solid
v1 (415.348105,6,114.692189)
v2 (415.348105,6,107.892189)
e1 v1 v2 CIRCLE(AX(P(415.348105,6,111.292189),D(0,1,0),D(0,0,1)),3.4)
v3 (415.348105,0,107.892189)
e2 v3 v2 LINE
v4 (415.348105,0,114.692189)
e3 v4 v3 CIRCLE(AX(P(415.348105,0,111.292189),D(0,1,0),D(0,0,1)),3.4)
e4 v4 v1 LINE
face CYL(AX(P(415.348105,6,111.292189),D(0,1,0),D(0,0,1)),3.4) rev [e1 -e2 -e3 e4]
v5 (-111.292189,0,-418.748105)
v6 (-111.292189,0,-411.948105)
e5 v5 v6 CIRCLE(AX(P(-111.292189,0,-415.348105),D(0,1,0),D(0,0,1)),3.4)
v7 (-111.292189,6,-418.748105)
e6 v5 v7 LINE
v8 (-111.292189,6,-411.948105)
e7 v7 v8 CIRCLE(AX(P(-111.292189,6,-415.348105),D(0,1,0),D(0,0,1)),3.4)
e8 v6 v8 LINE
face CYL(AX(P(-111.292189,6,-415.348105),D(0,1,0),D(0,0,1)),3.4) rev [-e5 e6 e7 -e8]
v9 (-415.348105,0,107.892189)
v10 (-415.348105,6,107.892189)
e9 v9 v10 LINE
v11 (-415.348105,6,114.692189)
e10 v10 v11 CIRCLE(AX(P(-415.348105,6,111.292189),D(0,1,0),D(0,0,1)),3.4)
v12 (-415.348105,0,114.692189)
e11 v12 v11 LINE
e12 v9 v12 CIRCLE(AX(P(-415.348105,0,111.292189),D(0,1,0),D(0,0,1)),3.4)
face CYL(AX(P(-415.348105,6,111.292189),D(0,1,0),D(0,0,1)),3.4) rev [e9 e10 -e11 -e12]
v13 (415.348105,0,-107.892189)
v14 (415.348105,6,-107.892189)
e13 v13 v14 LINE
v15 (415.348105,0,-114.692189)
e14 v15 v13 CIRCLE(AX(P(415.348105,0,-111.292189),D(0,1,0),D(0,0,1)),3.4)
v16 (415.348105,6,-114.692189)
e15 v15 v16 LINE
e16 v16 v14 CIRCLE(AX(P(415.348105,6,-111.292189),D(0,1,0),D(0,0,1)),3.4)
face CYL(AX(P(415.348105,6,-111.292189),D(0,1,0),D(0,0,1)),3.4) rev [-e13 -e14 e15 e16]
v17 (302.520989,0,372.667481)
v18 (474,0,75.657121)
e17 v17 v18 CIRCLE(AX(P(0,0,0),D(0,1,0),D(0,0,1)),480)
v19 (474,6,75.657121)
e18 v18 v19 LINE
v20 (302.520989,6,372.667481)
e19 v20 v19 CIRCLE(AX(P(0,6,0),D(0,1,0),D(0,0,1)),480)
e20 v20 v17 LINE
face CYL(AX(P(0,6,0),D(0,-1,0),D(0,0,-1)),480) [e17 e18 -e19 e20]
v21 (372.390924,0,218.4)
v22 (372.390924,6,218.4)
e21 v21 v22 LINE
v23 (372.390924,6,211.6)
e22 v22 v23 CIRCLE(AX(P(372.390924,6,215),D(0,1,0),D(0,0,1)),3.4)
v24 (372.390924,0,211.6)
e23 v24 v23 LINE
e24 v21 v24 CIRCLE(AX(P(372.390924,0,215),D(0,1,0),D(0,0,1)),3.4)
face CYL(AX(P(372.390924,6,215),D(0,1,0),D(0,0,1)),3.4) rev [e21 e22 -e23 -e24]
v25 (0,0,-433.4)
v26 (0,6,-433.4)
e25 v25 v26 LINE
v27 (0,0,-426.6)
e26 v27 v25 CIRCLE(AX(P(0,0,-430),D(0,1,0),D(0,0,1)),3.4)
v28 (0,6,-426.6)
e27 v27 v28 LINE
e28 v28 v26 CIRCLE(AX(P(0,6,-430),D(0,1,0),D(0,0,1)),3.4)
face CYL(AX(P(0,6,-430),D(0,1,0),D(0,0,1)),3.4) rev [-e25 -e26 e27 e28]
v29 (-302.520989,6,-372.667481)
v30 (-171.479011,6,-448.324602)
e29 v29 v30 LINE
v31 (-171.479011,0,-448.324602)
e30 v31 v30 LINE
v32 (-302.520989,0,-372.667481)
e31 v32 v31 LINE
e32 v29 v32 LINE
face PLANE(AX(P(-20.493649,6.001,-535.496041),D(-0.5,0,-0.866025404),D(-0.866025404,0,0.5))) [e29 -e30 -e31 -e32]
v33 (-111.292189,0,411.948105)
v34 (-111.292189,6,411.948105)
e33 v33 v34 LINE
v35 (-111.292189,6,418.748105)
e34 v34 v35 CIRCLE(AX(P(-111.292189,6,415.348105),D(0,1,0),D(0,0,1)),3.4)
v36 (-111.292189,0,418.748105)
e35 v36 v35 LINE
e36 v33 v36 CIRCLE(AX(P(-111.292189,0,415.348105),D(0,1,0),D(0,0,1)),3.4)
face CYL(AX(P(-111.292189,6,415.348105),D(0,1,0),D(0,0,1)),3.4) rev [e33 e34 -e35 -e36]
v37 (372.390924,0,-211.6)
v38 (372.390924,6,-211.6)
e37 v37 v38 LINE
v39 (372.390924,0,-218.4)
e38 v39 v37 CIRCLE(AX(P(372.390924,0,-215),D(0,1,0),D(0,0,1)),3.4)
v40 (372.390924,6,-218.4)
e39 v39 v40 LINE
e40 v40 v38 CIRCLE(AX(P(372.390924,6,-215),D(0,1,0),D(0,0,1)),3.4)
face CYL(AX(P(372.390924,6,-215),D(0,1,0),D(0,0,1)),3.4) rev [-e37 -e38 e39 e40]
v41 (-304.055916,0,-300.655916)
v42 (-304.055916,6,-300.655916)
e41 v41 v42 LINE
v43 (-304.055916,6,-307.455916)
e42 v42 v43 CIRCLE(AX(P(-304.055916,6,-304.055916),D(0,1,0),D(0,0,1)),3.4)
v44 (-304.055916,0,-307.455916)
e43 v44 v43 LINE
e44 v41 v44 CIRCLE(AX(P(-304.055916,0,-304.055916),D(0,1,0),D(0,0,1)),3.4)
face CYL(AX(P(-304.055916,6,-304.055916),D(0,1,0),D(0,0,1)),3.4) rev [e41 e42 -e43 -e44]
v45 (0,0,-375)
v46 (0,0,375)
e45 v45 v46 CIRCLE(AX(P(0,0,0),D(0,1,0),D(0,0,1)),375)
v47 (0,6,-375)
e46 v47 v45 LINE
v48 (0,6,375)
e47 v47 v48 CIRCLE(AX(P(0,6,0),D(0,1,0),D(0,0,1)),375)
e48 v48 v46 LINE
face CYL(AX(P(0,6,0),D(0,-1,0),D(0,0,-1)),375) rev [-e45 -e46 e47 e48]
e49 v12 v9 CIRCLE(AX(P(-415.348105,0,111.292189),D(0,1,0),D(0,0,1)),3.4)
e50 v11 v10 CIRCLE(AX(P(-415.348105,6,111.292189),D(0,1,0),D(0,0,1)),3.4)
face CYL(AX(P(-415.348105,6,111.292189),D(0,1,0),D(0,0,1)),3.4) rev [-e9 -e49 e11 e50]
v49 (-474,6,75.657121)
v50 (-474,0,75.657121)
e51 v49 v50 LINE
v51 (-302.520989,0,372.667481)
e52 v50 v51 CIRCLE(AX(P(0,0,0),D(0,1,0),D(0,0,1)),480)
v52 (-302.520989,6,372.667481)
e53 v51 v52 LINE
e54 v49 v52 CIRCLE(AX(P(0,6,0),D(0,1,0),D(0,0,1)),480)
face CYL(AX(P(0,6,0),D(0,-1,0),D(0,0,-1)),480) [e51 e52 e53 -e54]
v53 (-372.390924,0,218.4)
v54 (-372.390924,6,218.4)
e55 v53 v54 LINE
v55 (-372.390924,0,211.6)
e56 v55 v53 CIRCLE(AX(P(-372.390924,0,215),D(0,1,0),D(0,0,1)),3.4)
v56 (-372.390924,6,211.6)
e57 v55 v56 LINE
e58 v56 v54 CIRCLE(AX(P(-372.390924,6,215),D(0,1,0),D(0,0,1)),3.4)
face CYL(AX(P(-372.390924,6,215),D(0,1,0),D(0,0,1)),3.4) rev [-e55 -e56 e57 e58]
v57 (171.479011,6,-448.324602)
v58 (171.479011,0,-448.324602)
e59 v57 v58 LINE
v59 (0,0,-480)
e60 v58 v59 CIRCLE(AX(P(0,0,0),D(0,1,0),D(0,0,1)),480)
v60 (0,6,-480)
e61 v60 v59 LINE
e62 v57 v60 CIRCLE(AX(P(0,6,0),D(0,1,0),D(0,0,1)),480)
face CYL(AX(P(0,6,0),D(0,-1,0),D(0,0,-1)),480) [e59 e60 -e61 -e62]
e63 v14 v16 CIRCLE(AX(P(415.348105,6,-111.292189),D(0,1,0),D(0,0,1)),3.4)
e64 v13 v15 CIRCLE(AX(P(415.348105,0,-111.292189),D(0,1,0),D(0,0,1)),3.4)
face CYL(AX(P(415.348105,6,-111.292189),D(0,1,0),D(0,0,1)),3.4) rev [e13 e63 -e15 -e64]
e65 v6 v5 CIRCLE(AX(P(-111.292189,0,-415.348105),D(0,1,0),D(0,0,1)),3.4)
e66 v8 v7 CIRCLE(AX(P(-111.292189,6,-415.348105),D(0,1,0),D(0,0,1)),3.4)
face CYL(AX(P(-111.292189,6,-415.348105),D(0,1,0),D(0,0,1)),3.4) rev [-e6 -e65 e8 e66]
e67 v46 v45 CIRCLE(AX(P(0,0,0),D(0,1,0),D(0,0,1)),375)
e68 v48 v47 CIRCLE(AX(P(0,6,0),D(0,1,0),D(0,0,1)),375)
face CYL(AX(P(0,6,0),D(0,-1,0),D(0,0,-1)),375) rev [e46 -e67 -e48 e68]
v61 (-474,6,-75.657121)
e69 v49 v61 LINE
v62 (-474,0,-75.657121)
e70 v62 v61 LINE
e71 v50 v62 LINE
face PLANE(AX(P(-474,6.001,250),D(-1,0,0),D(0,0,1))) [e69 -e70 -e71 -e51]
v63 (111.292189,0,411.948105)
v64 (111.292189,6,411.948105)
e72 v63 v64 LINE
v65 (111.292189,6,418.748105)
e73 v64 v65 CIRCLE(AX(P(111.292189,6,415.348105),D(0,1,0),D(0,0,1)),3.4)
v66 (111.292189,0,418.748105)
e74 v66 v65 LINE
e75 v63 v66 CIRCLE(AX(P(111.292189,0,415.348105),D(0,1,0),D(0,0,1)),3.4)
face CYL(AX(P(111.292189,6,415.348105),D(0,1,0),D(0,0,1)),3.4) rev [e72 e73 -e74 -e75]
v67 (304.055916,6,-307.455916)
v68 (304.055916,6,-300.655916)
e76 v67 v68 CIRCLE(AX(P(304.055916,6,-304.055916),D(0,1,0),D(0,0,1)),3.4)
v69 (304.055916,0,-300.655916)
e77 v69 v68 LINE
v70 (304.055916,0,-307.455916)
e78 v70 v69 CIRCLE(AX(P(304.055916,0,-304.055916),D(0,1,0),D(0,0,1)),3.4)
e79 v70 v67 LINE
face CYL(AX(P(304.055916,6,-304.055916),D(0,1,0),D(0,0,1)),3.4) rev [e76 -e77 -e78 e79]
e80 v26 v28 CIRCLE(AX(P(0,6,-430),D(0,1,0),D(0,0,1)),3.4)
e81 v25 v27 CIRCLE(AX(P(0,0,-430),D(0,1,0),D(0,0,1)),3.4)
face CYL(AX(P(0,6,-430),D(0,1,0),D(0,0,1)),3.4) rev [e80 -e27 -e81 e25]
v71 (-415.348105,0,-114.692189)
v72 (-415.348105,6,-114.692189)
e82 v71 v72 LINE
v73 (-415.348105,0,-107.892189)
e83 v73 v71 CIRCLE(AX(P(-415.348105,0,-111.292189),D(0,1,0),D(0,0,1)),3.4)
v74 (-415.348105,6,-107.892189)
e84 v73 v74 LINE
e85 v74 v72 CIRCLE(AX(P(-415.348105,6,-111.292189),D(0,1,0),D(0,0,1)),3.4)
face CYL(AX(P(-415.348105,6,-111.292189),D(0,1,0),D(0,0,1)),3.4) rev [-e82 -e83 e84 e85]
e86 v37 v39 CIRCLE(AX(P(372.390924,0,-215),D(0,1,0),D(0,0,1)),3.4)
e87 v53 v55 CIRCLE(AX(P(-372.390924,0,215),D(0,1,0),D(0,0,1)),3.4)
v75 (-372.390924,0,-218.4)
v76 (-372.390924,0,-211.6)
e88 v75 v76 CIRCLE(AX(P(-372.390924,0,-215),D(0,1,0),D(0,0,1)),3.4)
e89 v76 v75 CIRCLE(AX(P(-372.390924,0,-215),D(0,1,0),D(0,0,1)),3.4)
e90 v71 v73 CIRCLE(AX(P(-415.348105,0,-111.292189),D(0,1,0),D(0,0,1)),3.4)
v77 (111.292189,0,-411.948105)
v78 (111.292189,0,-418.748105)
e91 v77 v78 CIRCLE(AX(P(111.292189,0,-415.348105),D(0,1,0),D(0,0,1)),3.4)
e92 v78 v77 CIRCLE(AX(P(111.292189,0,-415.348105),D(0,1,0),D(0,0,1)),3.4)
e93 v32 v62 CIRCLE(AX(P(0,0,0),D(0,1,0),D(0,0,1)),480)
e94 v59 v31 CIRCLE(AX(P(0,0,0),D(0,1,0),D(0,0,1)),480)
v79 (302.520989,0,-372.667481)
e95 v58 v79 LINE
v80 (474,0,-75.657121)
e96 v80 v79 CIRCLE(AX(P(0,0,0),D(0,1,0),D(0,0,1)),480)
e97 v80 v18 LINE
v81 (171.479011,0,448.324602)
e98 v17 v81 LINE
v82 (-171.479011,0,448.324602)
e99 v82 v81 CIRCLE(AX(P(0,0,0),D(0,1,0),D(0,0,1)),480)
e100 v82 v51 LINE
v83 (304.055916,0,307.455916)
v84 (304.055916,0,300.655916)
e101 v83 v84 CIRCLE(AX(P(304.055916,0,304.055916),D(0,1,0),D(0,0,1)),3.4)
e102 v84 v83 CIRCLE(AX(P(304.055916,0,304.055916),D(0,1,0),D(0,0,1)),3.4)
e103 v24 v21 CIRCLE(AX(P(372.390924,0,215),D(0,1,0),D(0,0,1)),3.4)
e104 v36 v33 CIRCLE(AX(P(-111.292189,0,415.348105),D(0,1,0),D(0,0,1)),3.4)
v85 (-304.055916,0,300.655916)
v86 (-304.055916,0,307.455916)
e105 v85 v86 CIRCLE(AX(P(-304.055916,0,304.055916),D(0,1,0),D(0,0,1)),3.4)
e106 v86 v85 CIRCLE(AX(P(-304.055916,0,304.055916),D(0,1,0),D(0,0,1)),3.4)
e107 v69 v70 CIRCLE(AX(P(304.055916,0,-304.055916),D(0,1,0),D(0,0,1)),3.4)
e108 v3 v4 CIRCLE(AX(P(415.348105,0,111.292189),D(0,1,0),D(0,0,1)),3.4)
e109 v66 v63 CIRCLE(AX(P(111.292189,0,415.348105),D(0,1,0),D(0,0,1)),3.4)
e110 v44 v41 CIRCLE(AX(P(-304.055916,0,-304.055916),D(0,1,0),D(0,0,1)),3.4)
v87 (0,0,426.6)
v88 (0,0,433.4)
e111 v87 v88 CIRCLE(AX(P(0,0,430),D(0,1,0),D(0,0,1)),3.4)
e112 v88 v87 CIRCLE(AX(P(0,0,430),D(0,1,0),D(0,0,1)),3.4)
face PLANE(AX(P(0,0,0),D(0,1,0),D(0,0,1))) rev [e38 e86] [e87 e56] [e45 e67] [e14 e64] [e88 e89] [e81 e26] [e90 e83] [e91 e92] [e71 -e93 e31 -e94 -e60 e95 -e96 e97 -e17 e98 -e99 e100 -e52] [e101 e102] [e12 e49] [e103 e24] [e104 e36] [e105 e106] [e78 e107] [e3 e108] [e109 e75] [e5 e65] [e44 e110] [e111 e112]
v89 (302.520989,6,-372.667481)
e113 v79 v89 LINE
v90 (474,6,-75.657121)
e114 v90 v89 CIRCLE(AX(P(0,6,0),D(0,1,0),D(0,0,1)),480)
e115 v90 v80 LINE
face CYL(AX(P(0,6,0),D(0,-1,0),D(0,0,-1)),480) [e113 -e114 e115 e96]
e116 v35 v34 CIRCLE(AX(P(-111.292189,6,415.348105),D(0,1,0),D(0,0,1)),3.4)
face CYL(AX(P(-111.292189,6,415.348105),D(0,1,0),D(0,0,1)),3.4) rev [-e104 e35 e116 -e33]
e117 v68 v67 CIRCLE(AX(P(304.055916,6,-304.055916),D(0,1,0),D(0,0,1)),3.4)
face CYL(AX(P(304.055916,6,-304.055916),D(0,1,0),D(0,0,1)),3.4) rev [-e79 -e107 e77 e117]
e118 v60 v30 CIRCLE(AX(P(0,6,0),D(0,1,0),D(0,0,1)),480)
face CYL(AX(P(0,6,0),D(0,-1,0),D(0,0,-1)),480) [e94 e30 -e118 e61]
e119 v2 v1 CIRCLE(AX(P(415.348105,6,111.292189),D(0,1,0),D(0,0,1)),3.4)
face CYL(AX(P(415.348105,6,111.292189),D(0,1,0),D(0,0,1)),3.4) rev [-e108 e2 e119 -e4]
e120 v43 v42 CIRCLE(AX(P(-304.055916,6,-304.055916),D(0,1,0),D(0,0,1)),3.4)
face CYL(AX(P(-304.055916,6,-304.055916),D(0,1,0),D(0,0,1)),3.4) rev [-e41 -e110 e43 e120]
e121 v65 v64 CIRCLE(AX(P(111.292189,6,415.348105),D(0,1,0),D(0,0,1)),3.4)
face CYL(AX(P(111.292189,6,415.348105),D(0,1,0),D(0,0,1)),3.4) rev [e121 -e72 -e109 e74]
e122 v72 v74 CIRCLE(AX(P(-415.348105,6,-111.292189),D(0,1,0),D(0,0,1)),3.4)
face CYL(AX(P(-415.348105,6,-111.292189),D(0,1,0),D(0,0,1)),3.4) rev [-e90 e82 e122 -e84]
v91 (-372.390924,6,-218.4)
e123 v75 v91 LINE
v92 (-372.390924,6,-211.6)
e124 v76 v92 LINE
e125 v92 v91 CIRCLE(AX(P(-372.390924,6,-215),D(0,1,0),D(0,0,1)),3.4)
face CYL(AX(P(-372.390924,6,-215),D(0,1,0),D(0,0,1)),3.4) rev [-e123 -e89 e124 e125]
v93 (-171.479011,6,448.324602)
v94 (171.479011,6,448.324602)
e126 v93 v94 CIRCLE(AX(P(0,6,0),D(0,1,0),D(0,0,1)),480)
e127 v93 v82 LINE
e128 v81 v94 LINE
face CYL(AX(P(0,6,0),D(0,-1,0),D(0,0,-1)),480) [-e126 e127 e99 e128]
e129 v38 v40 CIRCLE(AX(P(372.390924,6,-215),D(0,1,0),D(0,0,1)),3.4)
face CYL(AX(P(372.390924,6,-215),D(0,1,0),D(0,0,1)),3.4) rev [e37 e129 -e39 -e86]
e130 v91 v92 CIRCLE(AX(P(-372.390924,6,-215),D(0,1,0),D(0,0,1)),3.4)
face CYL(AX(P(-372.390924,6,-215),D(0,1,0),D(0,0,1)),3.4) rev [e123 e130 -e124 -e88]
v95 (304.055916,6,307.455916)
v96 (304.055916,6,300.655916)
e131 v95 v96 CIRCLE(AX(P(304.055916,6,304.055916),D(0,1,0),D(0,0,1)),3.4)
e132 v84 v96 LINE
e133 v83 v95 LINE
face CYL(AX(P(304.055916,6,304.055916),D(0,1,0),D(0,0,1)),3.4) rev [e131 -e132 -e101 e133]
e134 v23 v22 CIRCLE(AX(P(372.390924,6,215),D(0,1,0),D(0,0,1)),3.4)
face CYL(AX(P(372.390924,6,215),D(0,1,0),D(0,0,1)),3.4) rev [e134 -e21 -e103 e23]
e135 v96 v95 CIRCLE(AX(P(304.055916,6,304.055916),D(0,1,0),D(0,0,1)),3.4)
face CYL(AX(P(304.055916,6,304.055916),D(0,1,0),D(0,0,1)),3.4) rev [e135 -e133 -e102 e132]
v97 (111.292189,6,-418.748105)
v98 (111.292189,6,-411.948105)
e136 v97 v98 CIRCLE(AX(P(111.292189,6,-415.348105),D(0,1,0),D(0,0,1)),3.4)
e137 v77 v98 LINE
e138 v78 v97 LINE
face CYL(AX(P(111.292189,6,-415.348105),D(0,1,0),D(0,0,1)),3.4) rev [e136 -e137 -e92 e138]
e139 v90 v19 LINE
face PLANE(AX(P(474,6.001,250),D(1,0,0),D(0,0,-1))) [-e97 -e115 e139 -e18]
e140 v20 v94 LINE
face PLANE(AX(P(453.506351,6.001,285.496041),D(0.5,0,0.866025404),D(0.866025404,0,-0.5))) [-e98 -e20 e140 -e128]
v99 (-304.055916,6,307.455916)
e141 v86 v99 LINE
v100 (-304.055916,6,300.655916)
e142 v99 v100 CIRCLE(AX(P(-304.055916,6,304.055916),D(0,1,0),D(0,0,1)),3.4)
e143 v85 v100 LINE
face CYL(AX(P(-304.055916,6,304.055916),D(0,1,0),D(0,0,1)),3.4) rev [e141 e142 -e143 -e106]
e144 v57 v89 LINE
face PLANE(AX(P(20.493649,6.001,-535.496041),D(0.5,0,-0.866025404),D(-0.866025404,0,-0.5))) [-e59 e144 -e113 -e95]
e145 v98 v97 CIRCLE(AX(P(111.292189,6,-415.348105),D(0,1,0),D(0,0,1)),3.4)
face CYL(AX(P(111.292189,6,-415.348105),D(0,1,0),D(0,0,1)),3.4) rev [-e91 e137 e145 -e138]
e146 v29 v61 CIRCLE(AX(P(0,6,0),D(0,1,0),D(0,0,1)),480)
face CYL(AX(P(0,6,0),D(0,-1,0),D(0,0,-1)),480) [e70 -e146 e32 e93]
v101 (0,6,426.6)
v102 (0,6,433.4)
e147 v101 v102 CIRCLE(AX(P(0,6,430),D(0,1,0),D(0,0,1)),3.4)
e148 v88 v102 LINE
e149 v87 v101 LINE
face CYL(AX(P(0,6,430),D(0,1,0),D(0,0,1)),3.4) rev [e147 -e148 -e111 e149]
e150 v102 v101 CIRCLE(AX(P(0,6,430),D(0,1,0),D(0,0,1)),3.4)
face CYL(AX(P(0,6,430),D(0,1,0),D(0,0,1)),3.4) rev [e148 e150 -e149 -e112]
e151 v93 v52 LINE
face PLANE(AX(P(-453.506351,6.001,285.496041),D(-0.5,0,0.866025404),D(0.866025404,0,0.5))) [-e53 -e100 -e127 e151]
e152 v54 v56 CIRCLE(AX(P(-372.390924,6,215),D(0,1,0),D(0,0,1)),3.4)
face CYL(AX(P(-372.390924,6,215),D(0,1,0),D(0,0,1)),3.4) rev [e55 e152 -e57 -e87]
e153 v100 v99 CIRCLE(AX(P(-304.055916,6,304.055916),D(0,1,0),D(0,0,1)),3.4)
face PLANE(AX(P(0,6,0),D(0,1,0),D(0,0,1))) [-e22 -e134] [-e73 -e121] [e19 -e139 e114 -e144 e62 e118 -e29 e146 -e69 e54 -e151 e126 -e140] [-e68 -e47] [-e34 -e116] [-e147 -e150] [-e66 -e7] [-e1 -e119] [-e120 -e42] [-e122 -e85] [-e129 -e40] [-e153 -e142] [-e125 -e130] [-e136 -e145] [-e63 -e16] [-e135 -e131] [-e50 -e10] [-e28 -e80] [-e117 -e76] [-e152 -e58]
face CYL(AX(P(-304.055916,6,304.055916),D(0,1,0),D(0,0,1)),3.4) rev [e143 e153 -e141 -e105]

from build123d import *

# Parameters (mm, degrees)
SKETCH1_R             = 480
SKETCH1_R_2           = 375
BOSS_EXTRUDE1_DEPTH   = 6
CUT_EXTRUDE3_REACH    = 680.849
SKETCH2_W             = 12
SKETCH2_H             = 500
CIRPATTERN1_COUNT     = 3
M8_TAPPED_HOLE1_D     = 6.8
M8_TAPPED_HOLE1_DEPTH = 6


with BuildPart() as part:
    # Sketch1 → Boss-Extrude1 (new body)
    with BuildSketch(Plane(origin=(0, 0, 0), x_dir=(1, 0, 0), z_dir=(0, 1, 0))):
        with Locations(Location((0, 0, 0), (0, 0, 270))):
            Circle(SKETCH1_R)
        with Locations(Location((0, 0, 0), (0, 0, 270))):
            Circle(SKETCH1_R_2, mode=Mode.SUBTRACT)
    extrude(amount=BOSS_EXTRUDE1_DEPTH)

    # Sketch2 → Cut-Extrude3 (cut, up to next)
    with BuildSketch(Plane(origin=(0, 0, 0), x_dir=(1, 0, 0), z_dir=(0, 1, 0)), mode=Mode.PRIVATE) as cut_extrude3_sk1:
        with Locations((-480, 0)):
            Rectangle(SKETCH2_W, SKETCH2_H)
    cut_extrude3_tool1 = extrude(cut_extrude3_sk1.sketch, amount=CUT_EXTRUDE3_REACH, mode=Mode.PRIVATE) & part.part
    # Sketch2 → Cut-Extrude3 (cut, up to next)
    with BuildSketch(Plane(origin=(0, 0, 0), x_dir=(1, 0, 0), z_dir=(0, 1, 0)), mode=Mode.PRIVATE) as cut_extrude3_sk2:
        with Locations((480, 0)):
            Rectangle(SKETCH2_W, SKETCH2_H)
    cut_extrude3_tool2 = extrude(cut_extrude3_sk2.sketch, amount=CUT_EXTRUDE3_REACH, mode=Mode.PRIVATE) & part.part
    cut_extrude3_1 = cut_extrude3_tool1.solids().sort_by_distance((-480, 0, 0))[0]
    add(cut_extrude3_1, mode=Mode.SUBTRACT)
    cut_extrude3_2 = cut_extrude3_tool2.solids().sort_by_distance((480, 0, 0))[0]
    add(cut_extrude3_2, mode=Mode.SUBTRACT)
    cut_extrude3 = cut_extrude3_1 + cut_extrude3_2  # Cut-Extrude3 as one shape, for the pattern or mirror that repeats it

    # CirPattern1: Cut-Extrude3 ×3 about axis
    cirpattern1_axis = Axis((0, 0, 0), (0, 1, 0))
    for i in range(1, CIRPATTERN1_COUNT):
        add(cut_extrude3.rotate(cirpattern1_axis, i * 360 / CIRPATTERN1_COUNT), mode=Mode.SUBTRACT)

    # M8 Tapped Hole1
    with Locations(Plane(origin=(0, 6, 0), x_dir=(1, 0, 0), z_dir=(0, 1, 0))):
        with Locations((0, 430), (111.292189394, 415.348105304), (-111.292189394, 415.348105304), (372.390923627, 215), (415.348105304, 111.292189394), (304.05591591, 304.05591591), (372.390923627, -215), (304.05591591, -304.05591591), (415.348105304, -111.292189394), (0, -430), (-111.292189394, -415.348105304), (111.292189394, -415.348105304), (-372.390923627, -215), (-415.348105304, -111.292189394), (-304.05591591, -304.05591591), (-372.390923627, 215), (-304.05591591, 304.05591591), (-415.348105304, 111.292189394), (0, 0)):
            Hole(M8_TAPPED_HOLE1_D / 2, depth=M8_TAPPED_HOLE1_DEPTH)


solid = part.part
